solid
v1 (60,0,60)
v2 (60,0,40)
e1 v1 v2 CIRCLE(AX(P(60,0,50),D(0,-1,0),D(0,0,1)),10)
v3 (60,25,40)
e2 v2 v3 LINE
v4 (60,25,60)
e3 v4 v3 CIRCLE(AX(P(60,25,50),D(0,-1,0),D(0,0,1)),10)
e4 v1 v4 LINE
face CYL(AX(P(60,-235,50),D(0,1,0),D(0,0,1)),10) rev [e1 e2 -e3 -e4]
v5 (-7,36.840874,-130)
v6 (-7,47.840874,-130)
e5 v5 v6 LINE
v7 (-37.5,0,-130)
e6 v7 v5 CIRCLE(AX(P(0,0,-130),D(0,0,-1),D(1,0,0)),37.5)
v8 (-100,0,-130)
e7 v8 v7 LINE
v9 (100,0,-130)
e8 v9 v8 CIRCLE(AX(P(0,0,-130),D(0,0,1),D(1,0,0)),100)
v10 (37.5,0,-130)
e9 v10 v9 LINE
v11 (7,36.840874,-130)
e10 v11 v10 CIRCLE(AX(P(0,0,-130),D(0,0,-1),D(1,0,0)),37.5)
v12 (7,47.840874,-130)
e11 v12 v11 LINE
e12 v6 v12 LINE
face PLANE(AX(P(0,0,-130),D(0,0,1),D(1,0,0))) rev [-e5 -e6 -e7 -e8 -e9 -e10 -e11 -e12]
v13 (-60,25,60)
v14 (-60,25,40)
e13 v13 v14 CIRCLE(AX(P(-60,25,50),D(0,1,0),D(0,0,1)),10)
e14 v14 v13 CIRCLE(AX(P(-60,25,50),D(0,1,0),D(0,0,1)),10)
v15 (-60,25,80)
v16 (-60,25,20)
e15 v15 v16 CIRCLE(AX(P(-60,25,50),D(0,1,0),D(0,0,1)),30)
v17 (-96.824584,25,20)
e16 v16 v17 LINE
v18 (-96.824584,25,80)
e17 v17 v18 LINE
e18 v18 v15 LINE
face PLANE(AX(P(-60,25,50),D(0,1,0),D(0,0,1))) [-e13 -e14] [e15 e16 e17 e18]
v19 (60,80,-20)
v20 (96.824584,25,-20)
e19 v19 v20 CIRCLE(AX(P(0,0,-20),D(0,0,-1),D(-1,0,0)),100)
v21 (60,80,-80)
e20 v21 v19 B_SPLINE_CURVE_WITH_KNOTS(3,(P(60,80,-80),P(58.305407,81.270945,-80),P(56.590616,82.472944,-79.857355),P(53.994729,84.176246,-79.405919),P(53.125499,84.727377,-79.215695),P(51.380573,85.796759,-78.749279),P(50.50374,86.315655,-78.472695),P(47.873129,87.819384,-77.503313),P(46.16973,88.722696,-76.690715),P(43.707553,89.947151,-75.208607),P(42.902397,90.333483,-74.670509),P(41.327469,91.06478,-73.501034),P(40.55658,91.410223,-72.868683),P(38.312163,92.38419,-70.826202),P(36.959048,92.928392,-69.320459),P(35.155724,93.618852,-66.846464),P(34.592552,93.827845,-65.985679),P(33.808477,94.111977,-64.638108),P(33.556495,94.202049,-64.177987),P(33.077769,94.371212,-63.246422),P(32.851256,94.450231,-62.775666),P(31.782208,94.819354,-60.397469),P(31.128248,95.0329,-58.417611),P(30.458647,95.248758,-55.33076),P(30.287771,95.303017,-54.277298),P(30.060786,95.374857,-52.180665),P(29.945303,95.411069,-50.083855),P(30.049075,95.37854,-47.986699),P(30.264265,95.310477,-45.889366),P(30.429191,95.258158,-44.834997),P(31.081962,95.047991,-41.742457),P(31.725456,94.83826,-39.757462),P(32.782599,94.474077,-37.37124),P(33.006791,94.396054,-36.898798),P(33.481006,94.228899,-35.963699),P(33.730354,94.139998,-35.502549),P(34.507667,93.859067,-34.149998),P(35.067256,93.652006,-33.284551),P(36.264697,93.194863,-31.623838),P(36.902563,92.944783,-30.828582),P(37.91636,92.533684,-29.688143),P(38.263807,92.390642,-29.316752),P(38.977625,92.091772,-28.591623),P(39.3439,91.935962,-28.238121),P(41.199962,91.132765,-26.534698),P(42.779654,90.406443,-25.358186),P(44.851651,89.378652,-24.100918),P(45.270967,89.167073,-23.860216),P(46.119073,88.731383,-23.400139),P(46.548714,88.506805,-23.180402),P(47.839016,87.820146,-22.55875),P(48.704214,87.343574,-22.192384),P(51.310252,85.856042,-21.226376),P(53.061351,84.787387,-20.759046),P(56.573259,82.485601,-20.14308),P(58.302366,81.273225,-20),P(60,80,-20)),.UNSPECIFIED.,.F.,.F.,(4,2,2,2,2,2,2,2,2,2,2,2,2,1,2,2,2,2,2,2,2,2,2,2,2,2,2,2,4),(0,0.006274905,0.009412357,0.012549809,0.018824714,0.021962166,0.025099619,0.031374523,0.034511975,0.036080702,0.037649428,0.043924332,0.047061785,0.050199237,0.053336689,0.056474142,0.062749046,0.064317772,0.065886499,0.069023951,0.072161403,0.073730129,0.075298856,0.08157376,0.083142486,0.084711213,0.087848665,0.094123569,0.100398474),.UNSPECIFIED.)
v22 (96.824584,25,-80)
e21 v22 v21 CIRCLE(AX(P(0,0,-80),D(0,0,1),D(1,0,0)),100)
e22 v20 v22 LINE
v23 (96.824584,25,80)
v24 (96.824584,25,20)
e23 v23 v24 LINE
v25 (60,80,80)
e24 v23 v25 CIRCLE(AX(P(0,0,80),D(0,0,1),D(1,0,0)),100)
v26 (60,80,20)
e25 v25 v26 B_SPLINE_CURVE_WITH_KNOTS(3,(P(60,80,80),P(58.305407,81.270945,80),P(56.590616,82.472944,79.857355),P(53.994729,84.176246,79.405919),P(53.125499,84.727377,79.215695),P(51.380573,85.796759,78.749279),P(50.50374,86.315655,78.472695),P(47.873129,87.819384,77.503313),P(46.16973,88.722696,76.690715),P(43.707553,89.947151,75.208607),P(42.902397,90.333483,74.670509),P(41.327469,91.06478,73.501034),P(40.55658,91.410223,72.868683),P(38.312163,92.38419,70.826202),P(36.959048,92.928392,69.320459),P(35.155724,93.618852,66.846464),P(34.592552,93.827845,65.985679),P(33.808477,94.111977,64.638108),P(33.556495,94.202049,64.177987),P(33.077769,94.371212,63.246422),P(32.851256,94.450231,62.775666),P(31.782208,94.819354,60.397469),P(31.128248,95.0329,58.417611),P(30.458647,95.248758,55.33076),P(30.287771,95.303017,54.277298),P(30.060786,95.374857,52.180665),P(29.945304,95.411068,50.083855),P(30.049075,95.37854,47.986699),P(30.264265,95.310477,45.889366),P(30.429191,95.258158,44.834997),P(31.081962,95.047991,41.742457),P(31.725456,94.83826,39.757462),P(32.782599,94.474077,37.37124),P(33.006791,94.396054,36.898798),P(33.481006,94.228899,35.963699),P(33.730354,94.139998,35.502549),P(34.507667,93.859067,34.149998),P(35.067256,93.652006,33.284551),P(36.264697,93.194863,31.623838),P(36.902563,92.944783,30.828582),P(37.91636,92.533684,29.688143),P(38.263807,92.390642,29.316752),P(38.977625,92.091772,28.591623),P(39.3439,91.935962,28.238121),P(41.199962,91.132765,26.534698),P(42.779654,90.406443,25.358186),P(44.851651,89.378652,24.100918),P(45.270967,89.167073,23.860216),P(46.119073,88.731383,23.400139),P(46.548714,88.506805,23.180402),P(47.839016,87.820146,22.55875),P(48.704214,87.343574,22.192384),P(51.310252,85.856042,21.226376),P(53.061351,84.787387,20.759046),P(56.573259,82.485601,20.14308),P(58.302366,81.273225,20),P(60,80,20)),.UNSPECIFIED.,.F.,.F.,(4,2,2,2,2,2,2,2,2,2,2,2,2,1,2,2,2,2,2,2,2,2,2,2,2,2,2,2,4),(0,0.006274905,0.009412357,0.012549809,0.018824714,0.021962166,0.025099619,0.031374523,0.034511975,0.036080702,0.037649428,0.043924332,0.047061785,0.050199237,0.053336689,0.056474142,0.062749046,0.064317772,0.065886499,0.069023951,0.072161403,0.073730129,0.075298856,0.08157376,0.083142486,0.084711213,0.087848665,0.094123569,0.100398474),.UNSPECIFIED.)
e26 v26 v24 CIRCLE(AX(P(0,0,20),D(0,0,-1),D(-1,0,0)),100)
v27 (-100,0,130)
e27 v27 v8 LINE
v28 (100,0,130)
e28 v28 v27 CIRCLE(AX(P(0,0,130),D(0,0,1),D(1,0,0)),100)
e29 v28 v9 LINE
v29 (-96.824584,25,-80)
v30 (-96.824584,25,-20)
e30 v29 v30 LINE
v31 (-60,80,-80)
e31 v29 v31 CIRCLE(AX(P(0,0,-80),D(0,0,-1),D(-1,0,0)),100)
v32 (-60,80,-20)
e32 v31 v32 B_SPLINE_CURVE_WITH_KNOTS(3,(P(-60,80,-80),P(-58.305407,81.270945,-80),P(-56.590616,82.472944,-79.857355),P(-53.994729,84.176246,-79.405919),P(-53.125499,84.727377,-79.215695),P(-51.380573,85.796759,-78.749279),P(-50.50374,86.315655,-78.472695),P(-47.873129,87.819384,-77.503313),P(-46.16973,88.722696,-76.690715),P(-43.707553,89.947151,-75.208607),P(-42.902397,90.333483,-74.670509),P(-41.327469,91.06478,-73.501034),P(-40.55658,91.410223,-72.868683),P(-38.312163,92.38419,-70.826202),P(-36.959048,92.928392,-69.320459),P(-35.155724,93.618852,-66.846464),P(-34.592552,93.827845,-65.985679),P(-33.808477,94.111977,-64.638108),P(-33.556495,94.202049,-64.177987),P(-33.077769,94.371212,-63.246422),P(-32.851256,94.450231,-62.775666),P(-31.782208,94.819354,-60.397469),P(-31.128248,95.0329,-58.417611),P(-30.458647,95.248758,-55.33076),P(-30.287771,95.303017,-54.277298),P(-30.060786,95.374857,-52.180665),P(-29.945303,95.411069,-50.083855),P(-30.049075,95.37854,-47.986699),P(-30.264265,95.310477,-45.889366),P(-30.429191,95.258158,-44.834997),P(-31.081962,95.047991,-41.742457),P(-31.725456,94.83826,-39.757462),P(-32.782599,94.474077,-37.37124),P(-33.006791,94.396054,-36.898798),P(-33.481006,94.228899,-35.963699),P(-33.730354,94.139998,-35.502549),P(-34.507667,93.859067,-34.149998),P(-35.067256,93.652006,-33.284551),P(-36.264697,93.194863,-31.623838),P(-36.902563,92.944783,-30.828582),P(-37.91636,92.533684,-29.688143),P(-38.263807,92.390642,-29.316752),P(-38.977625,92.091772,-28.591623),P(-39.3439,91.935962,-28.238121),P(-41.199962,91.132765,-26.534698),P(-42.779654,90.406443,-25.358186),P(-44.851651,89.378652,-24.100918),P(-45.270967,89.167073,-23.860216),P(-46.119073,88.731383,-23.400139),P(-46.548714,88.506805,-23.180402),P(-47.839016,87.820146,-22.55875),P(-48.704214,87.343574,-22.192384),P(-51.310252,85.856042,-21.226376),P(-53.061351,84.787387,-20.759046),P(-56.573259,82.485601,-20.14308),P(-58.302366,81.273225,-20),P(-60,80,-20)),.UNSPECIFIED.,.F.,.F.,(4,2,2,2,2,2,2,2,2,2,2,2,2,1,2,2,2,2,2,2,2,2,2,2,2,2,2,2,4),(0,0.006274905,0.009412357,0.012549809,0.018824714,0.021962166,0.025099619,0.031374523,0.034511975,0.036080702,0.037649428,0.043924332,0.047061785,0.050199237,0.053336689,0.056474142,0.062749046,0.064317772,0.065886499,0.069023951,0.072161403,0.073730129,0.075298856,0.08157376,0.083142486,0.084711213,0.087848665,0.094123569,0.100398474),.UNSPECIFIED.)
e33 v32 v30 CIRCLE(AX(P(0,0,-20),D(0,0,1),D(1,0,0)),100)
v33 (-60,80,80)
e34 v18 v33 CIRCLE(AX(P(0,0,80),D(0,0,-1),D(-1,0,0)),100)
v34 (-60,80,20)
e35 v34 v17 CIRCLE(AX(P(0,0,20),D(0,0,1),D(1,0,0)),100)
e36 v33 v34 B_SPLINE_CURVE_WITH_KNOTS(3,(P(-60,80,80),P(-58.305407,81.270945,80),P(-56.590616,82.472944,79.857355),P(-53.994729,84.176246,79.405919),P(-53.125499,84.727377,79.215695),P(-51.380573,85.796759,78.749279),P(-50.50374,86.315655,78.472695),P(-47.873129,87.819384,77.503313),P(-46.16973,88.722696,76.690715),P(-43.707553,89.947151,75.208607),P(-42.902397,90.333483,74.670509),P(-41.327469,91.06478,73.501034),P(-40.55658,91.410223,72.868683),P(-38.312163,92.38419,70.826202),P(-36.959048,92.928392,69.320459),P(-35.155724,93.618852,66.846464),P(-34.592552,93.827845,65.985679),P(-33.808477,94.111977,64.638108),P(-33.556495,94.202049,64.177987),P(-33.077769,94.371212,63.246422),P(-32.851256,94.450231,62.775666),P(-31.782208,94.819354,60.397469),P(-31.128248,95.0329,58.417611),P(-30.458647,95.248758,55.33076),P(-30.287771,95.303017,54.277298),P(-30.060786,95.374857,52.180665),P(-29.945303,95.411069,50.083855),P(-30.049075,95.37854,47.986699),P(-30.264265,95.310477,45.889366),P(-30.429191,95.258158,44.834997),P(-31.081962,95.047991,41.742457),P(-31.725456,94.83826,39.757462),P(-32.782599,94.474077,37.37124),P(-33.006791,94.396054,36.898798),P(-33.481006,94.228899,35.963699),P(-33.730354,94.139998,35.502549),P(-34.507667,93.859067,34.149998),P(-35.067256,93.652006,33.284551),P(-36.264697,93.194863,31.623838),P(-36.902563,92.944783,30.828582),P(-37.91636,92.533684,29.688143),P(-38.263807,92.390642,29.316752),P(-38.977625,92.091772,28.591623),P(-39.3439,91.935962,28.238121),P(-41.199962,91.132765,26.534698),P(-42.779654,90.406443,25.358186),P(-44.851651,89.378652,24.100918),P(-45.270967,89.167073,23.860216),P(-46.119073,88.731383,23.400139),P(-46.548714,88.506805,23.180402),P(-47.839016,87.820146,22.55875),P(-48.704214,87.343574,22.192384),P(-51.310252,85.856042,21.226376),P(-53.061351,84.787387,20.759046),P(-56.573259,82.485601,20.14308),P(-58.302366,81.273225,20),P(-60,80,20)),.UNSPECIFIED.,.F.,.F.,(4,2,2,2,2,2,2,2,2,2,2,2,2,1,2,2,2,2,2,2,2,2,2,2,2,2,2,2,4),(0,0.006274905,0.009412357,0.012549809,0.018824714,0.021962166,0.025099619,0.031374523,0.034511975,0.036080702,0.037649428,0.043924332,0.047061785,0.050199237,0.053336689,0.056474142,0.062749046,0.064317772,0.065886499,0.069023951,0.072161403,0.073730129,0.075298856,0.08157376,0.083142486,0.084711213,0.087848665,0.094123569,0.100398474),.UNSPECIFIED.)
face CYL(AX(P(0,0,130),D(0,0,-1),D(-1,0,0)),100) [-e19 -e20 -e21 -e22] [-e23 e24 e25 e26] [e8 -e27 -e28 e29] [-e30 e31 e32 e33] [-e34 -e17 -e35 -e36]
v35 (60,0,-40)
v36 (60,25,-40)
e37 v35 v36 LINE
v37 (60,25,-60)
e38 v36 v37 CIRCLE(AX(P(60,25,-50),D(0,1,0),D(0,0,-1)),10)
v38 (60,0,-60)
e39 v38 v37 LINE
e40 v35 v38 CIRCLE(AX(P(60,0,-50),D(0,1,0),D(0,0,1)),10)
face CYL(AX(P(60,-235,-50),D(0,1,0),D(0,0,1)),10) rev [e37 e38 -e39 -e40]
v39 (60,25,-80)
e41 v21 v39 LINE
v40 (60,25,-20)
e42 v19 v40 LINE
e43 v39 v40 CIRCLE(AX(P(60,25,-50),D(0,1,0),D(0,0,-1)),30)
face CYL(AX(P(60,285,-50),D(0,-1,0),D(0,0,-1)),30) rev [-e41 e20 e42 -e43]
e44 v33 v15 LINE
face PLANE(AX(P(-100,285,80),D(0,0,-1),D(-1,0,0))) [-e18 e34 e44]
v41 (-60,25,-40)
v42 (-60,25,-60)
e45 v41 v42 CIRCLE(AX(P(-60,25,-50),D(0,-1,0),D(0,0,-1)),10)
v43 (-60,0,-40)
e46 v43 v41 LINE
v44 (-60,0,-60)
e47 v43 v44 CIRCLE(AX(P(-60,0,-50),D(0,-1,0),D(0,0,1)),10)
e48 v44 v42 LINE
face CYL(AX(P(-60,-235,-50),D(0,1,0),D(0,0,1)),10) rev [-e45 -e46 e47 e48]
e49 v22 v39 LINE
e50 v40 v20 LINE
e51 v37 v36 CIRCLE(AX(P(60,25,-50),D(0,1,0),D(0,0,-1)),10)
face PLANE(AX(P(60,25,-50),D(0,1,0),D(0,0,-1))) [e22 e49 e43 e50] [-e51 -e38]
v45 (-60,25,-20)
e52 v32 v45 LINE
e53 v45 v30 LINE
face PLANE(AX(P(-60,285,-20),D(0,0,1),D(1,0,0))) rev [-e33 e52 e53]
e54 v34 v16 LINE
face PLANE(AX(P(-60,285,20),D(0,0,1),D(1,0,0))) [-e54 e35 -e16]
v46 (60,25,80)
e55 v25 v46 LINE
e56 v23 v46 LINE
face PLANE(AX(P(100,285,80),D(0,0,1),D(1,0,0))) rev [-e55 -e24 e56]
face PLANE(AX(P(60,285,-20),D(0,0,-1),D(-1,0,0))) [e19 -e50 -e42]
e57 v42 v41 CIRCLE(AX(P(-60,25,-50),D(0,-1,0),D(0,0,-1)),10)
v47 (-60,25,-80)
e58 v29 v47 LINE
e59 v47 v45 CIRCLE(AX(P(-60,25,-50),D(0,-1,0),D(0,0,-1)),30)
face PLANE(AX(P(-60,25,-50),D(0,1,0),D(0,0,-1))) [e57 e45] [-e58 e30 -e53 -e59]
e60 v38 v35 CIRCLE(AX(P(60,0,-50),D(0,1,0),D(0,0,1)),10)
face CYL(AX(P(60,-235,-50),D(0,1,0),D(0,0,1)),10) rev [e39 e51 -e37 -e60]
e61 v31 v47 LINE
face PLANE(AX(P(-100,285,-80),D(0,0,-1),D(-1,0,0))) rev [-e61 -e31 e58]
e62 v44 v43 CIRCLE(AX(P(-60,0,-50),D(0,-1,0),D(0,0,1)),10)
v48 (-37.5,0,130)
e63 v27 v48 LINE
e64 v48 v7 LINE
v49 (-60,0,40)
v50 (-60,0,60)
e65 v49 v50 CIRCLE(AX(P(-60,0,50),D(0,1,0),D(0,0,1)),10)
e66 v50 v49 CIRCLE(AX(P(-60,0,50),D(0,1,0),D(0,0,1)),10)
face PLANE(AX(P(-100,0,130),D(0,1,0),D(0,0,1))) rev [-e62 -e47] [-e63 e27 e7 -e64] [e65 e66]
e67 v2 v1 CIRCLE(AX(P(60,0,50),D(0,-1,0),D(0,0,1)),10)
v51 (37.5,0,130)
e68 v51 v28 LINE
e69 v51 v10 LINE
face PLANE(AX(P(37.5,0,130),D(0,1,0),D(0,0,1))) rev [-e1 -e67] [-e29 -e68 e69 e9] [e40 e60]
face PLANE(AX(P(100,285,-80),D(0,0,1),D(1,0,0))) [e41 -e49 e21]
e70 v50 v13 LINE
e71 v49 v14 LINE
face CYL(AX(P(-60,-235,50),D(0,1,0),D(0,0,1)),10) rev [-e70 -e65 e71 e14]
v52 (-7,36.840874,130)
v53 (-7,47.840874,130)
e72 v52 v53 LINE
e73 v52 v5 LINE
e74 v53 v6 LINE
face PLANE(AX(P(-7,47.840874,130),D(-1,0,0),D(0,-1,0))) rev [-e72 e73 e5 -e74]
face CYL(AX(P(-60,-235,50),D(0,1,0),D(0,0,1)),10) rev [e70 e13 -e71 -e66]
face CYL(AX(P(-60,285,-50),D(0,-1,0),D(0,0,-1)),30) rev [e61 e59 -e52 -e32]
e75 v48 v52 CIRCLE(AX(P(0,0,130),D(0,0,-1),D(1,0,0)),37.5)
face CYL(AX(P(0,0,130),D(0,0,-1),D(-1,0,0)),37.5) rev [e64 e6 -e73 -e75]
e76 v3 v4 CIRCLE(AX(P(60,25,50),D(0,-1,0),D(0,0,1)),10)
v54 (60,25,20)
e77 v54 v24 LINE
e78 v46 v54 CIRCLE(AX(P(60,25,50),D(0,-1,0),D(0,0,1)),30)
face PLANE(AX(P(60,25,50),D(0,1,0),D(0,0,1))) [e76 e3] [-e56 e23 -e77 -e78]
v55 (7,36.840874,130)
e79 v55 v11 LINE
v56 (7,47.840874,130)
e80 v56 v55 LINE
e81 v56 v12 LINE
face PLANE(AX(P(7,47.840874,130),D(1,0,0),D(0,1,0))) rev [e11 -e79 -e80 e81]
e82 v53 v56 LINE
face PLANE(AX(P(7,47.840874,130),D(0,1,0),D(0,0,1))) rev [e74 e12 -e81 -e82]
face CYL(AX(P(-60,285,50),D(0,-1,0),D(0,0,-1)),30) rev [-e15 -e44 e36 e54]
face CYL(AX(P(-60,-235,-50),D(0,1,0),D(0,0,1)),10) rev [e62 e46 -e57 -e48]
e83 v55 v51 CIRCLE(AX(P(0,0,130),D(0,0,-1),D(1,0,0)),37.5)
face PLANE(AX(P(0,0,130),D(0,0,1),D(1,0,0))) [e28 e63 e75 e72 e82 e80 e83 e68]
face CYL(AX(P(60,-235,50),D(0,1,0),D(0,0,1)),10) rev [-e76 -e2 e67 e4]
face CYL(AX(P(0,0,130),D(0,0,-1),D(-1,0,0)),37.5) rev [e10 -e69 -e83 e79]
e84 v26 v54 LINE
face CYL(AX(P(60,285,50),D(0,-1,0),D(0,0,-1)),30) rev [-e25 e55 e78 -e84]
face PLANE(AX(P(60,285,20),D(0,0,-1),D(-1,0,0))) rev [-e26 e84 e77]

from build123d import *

# Parameters (mm, degrees)
HOUSING_BODY_DEPTH                     = 130
BOLT_START                             = 25
BOLT_POCKET_DEPTH                      = 260
BOLT_POCKET_MIRROR_RIGHT_COPY_1_DEPTH  = 260
BOLT_HOLE_SKETCH_R                     = 10
BOLT_HOLE_20_DEPTH                     = 260
BOLT_HOLE_MIRROR_RIGHT_COPY_1_SKETCH_R = 10
BOLT_HOLE_MIRROR_RIGHT_COPY_1_DEPTH    = 260
NOTCH_CUT_DEPTH                        = 296.972971894


with BuildPart() as part:
    # Housing Profile Sketch → Housing Body (new, symmetric)
    with BuildSketch(Plane.XY):
        with BuildLine():
            Line((-100, 0), (-37.5, 0))
            ThreePointArc((-37.5, 0), (0, 37.5), (37.5, 0))
            Line((37.5, 0), (100, 0))
            ThreePointArc((100, 0), (0, 100), (-100, 0))
        make_face()
    extrude(amount=HOUSING_BODY_DEPTH, both=True)

    # Bolt Pocket Sketch → Bolt Pocket (cut)
    with BuildSketch(Plane(origin=(0, 0, 0), x_dir=(1, 0, 0), z_dir=(0, 1, 0)).offset(BOLT_START)):
        with BuildLine():
            Line((-60, -20), (-100, -20))
            Line((-100, -20), (-100, -80))
            Line((-100, -80), (-60, -80))
            ThreePointArc((-60, -80), (-30, -50), (-60, -20))
        make_face()
    bolt_pocket = extrude(amount=BOLT_POCKET_DEPTH, mode=Mode.SUBTRACT)

    # Bolt Pocket Mirror Front: Bolt Pocket across plane
    add(bolt_pocket.mirror(Plane.XY), mode=Mode.SUBTRACT)

    # Bolt Pocket Mirror Right: Bolt Pocket across plane
    add(bolt_pocket.mirror(Plane(origin=(0, 0, 0), x_dir=(0, 0, 1), z_dir=(1, 0, 0))), mode=Mode.SUBTRACT)

    # Bolt Pocket Mirror Right copy 1 sketch → Bolt Pocket Mirror Right copy 1 (cut)
    with BuildSketch(Plane(origin=(0, 0, 0), x_dir=(-1, 0, 0), z_dir=(0, 1, 0)).offset(BOLT_START)):
        with BuildLine():
            Line((-60, -20), (-100, -20))
            Line((-100, -20), (-100, -80))
            Line((-100, -80), (-60, -80))
            ThreePointArc((-60, -80), (-30, -50), (-60, -20))
        make_face()
    extrude(amount=BOLT_POCKET_MIRROR_RIGHT_COPY_1_DEPTH, mode=Mode.SUBTRACT)

    # Bolt Hole Sketch → Bolt Hole Ø20 (cut)
    with BuildSketch(Plane(origin=(0, 25, 0), x_dir=(1, 0, 0), z_dir=(0, 1, 0))):
        with Locations(Location((-60, -50, 0), (0, 0, 270))):
            Circle(BOLT_HOLE_SKETCH_R)
    bolt_hole_20 = extrude(amount=-BOLT_HOLE_20_DEPTH, mode=Mode.SUBTRACT)

    # Bolt Hole Mirror Front: Bolt Hole Ø20 across plane
    add(bolt_hole_20.mirror(Plane.XY), mode=Mode.SUBTRACT)

    # Bolt Hole Mirror Right: Bolt Hole Ø20 across plane
    add(bolt_hole_20.mirror(Plane(origin=(0, 0, 0), x_dir=(0, 0, 1), z_dir=(1, 0, 0))), mode=Mode.SUBTRACT)

    # Bolt Hole Mirror Right copy 1 sketch → Bolt Hole Mirror Right copy 1 (cut)
    with BuildSketch(Plane(origin=(0, 25, 0), x_dir=(-1, 0, 0), z_dir=(0, 1, 0))):
        with Locations(Location((-60, -50, 0), (0, 0, 270))):
            Circle(BOLT_HOLE_MIRROR_RIGHT_COPY_1_SKETCH_R)
    extrude(amount=-BOLT_HOLE_MIRROR_RIGHT_COPY_1_DEPTH, mode=Mode.SUBTRACT)

    # Notch Sketch → Notch Cut (cut, through all)
    with BuildSketch(Plane(origin=(0, 0, -130), x_dir=(-1, 0, 0), z_dir=(0, 0, -1))):
        with BuildLine():
            Line((-7, 47.84087404), (7, 47.84087404))
            Line((7, 47.84087404), (7, 36.84087404))
            ThreePointArc((7, 36.84087404), (0, 37.5), (-7, 36.84087404))
            Line((-7, 36.84087404), (-7, 47.84087404))
        make_face()
    extrude(amount=-NOTCH_CUT_DEPTH, mode=Mode.SUBTRACT)


solid = part.part
